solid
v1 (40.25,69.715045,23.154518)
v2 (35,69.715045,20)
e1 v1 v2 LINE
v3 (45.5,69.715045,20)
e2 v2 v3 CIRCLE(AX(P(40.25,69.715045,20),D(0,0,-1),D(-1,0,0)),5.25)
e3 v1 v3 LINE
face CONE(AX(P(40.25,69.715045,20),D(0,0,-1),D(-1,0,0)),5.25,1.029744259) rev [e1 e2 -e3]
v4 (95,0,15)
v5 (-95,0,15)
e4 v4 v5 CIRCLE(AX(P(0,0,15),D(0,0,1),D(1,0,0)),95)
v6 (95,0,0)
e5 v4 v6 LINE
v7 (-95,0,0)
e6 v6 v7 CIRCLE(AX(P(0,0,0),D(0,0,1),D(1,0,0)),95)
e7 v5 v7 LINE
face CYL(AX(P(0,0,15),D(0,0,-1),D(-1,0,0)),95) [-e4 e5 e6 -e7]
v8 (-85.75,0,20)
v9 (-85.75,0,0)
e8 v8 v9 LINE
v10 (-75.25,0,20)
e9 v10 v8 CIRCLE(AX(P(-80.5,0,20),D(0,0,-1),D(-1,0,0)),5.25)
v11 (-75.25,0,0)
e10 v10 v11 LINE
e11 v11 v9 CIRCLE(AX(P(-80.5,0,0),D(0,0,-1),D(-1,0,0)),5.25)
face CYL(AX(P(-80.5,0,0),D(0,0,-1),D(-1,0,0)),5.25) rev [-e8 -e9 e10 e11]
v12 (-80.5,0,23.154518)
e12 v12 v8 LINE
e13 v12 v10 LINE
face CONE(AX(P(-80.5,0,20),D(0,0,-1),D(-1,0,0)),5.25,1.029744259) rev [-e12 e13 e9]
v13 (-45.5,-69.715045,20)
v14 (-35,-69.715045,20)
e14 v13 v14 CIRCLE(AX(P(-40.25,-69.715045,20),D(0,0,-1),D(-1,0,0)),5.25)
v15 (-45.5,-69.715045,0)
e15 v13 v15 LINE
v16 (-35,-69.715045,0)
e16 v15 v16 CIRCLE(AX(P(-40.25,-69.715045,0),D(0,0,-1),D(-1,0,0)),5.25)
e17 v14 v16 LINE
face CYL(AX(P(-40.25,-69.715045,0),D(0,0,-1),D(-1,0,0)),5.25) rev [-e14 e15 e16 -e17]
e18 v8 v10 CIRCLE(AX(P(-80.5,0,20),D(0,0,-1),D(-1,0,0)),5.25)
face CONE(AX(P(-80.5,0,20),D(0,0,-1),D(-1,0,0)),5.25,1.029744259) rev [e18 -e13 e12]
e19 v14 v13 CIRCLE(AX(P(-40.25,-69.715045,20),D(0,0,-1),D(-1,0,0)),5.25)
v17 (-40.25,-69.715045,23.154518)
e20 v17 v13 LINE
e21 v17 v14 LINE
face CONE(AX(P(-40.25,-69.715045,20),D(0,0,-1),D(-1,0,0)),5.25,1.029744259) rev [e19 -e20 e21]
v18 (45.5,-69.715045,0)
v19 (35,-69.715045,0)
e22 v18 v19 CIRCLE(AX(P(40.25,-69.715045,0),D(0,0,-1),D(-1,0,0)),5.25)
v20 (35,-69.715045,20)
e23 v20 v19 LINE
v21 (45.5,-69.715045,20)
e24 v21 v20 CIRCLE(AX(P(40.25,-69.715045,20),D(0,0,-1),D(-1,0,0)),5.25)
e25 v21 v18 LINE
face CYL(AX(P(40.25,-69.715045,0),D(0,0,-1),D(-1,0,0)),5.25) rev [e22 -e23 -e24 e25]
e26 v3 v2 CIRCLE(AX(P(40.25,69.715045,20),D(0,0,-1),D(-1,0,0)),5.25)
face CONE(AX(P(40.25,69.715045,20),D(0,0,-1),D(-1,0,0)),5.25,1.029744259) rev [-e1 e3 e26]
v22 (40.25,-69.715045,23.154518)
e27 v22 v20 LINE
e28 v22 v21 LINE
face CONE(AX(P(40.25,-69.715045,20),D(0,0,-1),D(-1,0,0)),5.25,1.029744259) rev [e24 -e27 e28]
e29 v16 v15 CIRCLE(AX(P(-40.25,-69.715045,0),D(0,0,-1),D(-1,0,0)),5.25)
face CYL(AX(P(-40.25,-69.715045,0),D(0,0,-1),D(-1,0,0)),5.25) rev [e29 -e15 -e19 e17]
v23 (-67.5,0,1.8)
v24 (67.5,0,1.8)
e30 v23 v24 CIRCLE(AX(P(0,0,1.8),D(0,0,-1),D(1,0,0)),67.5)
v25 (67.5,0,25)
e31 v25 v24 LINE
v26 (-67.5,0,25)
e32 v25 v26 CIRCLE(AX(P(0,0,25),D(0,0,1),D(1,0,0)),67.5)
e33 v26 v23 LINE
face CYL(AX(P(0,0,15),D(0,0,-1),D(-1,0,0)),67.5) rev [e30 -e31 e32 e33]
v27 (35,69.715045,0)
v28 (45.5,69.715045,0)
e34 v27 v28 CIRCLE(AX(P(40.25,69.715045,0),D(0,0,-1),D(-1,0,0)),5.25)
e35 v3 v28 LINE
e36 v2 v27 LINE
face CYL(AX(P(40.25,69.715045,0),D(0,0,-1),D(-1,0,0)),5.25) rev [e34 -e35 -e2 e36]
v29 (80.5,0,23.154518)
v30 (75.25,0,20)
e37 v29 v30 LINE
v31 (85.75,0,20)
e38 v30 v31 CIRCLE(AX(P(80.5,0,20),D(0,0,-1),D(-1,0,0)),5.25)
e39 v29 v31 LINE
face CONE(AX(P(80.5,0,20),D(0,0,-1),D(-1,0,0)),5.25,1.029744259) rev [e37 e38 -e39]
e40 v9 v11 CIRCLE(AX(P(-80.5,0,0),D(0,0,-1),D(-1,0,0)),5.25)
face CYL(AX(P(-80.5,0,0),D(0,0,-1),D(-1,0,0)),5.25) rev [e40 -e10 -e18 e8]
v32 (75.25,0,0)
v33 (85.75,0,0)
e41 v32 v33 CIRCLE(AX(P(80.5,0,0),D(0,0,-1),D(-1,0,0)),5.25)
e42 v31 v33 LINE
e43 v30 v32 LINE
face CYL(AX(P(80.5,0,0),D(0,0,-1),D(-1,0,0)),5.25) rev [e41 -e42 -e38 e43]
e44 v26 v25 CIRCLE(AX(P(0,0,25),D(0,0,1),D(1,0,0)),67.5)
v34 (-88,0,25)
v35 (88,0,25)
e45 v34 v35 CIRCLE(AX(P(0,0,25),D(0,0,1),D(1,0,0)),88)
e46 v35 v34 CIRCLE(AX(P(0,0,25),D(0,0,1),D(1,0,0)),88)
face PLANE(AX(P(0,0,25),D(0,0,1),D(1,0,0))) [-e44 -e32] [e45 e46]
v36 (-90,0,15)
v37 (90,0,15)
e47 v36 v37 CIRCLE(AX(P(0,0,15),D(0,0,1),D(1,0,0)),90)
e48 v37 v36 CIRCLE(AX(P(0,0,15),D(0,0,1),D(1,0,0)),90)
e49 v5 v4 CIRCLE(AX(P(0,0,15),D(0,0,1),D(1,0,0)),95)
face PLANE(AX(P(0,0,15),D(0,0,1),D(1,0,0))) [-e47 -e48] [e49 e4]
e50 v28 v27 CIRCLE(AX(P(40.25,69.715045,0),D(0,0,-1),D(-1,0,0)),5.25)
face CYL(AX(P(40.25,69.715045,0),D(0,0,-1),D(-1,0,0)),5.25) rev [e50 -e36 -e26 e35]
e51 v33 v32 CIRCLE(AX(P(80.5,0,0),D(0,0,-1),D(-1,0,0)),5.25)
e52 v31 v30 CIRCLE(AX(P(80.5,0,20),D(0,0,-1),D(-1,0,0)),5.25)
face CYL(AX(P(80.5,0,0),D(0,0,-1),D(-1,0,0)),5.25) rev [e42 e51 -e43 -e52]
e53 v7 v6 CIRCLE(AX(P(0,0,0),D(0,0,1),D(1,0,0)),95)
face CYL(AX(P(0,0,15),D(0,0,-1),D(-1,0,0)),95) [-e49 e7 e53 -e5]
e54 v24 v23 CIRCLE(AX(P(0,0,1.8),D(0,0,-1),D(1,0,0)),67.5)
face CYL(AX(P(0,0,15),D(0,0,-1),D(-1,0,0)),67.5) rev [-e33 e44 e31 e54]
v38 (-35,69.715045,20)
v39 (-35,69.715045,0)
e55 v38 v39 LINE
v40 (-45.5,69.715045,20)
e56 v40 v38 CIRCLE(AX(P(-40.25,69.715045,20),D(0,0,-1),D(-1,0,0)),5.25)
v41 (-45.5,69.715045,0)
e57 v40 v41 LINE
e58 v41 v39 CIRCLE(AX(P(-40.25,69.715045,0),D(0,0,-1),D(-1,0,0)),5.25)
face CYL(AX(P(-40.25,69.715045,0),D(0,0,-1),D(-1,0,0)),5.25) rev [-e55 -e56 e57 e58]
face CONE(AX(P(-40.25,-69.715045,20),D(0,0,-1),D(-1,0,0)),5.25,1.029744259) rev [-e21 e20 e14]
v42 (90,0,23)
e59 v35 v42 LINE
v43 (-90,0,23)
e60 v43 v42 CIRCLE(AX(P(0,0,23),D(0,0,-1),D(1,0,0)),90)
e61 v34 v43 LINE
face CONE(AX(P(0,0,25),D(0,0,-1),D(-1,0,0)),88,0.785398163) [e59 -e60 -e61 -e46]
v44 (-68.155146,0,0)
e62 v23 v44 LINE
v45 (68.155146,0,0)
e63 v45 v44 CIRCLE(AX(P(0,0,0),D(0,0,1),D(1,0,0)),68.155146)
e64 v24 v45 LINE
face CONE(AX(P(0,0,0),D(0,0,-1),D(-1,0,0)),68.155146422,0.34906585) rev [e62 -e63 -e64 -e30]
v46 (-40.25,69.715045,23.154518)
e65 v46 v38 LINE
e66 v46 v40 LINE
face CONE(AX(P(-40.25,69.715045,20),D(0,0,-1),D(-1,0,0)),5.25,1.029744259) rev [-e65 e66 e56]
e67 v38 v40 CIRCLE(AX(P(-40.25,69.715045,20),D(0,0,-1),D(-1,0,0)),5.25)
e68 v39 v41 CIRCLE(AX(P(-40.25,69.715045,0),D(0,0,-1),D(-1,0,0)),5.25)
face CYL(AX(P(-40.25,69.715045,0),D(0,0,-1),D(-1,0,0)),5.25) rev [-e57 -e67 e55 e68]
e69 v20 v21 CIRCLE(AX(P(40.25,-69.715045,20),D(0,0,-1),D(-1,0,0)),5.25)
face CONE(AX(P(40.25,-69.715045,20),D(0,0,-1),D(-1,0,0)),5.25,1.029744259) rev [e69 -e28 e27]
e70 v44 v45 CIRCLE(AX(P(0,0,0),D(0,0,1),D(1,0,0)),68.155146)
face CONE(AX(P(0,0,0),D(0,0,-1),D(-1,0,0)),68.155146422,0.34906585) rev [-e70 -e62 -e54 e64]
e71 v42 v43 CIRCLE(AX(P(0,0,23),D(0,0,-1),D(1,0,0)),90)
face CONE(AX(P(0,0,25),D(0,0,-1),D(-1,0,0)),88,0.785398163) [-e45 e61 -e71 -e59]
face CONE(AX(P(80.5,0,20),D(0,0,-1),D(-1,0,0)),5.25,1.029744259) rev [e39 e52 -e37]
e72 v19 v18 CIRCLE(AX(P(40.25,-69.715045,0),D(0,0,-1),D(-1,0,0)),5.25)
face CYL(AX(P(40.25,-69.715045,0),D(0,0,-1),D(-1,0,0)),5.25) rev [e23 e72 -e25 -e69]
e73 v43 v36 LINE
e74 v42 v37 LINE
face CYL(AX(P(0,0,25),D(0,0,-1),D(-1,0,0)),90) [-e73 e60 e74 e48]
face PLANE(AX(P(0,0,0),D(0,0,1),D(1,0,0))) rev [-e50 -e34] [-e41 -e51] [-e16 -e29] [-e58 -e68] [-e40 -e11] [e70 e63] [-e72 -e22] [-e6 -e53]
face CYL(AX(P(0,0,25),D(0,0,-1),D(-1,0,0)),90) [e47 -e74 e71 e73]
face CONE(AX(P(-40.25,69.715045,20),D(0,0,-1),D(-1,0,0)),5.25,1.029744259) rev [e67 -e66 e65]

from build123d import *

# Parameters (mm, degrees)
SKETCH1_R                  = 95
SKETCH1_R_2                = 67.5
BOSS_EXTRUDE1_DEPTH        = 15
SKETCH2_R                  = 90
SKETCH2_R_2                = 67.5
BOSS_EXTRUDE2_DEPTH        = 10
CHAMFER1_SIZE              = 2
CHAMFER2_SIZE              = 1.8
CHAMFER2_SIZE2             = 0.655146422
M12X1_5_TAPPED_HOLE1_D     = 10.5
M12X1_5_TAPPED_HOLE1_DEPTH = 20
M12X1_5_TAPPED_HOLE1_TIP   = 3.15451825


with BuildPart() as part:
    # Sketch1 → Boss-Extrude1 (new body)
    with BuildSketch(Plane.XY):
        Circle(SKETCH1_R)
        Circle(SKETCH1_R_2, mode=Mode.SUBTRACT)
    extrude(amount=BOSS_EXTRUDE1_DEPTH)

    # Sketch2 → Boss-Extrude2 (add)
    with BuildSketch(Plane.XY.offset(15)):
        Circle(SKETCH2_R)
        Circle(SKETCH2_R_2, mode=Mode.SUBTRACT)
    extrude(amount=BOSS_EXTRUDE2_DEPTH)

    # Chamfer1
    chamfer1_edges = [part.edges().sort_by_distance(p)[0] for p in [
        (-90, 0, 25),
    ]]
    chamfer(chamfer1_edges, length=CHAMFER1_SIZE)

    # Chamfer2
    chamfer2_edges = [part.edges().sort_by_distance(p)[0] for p in [
        (-67.5, 0, 0),
    ]]
    chamfer2_side = [part.faces().sort_by_distance(p)[0] for p in [
        (-67.5, 0, 12.5),
    ]]
    chamfer(chamfer2_edges, length=CHAMFER2_SIZE, length2=CHAMFER2_SIZE2, reference=chamfer2_side[0])

    # M12x1.5 Tapped Hole1
    with Locations(Plane(origin=(40.25, 69.715045005, 0), x_dir=(-1, 0, 0), z_dir=(0, 0, -1))):
        with Locations((0, 0), (80.5, 0), (120.75, -69.715045005), (80.5, -139.43009001), (-40.25, -69.715045005), (0, -139.43009001)):
            Hole(M12X1_5_TAPPED_HOLE1_D / 2, depth=M12X1_5_TAPPED_HOLE1_DEPTH)
            with Locations((0, 0, -(M12X1_5_TAPPED_HOLE1_DEPTH + M12X1_5_TAPPED_HOLE1_TIP / 2))):  # 118° drill point
                Cone(0, M12X1_5_TAPPED_HOLE1_D / 2, M12X1_5_TAPPED_HOLE1_TIP, mode=Mode.SUBTRACT)


solid = part.part
